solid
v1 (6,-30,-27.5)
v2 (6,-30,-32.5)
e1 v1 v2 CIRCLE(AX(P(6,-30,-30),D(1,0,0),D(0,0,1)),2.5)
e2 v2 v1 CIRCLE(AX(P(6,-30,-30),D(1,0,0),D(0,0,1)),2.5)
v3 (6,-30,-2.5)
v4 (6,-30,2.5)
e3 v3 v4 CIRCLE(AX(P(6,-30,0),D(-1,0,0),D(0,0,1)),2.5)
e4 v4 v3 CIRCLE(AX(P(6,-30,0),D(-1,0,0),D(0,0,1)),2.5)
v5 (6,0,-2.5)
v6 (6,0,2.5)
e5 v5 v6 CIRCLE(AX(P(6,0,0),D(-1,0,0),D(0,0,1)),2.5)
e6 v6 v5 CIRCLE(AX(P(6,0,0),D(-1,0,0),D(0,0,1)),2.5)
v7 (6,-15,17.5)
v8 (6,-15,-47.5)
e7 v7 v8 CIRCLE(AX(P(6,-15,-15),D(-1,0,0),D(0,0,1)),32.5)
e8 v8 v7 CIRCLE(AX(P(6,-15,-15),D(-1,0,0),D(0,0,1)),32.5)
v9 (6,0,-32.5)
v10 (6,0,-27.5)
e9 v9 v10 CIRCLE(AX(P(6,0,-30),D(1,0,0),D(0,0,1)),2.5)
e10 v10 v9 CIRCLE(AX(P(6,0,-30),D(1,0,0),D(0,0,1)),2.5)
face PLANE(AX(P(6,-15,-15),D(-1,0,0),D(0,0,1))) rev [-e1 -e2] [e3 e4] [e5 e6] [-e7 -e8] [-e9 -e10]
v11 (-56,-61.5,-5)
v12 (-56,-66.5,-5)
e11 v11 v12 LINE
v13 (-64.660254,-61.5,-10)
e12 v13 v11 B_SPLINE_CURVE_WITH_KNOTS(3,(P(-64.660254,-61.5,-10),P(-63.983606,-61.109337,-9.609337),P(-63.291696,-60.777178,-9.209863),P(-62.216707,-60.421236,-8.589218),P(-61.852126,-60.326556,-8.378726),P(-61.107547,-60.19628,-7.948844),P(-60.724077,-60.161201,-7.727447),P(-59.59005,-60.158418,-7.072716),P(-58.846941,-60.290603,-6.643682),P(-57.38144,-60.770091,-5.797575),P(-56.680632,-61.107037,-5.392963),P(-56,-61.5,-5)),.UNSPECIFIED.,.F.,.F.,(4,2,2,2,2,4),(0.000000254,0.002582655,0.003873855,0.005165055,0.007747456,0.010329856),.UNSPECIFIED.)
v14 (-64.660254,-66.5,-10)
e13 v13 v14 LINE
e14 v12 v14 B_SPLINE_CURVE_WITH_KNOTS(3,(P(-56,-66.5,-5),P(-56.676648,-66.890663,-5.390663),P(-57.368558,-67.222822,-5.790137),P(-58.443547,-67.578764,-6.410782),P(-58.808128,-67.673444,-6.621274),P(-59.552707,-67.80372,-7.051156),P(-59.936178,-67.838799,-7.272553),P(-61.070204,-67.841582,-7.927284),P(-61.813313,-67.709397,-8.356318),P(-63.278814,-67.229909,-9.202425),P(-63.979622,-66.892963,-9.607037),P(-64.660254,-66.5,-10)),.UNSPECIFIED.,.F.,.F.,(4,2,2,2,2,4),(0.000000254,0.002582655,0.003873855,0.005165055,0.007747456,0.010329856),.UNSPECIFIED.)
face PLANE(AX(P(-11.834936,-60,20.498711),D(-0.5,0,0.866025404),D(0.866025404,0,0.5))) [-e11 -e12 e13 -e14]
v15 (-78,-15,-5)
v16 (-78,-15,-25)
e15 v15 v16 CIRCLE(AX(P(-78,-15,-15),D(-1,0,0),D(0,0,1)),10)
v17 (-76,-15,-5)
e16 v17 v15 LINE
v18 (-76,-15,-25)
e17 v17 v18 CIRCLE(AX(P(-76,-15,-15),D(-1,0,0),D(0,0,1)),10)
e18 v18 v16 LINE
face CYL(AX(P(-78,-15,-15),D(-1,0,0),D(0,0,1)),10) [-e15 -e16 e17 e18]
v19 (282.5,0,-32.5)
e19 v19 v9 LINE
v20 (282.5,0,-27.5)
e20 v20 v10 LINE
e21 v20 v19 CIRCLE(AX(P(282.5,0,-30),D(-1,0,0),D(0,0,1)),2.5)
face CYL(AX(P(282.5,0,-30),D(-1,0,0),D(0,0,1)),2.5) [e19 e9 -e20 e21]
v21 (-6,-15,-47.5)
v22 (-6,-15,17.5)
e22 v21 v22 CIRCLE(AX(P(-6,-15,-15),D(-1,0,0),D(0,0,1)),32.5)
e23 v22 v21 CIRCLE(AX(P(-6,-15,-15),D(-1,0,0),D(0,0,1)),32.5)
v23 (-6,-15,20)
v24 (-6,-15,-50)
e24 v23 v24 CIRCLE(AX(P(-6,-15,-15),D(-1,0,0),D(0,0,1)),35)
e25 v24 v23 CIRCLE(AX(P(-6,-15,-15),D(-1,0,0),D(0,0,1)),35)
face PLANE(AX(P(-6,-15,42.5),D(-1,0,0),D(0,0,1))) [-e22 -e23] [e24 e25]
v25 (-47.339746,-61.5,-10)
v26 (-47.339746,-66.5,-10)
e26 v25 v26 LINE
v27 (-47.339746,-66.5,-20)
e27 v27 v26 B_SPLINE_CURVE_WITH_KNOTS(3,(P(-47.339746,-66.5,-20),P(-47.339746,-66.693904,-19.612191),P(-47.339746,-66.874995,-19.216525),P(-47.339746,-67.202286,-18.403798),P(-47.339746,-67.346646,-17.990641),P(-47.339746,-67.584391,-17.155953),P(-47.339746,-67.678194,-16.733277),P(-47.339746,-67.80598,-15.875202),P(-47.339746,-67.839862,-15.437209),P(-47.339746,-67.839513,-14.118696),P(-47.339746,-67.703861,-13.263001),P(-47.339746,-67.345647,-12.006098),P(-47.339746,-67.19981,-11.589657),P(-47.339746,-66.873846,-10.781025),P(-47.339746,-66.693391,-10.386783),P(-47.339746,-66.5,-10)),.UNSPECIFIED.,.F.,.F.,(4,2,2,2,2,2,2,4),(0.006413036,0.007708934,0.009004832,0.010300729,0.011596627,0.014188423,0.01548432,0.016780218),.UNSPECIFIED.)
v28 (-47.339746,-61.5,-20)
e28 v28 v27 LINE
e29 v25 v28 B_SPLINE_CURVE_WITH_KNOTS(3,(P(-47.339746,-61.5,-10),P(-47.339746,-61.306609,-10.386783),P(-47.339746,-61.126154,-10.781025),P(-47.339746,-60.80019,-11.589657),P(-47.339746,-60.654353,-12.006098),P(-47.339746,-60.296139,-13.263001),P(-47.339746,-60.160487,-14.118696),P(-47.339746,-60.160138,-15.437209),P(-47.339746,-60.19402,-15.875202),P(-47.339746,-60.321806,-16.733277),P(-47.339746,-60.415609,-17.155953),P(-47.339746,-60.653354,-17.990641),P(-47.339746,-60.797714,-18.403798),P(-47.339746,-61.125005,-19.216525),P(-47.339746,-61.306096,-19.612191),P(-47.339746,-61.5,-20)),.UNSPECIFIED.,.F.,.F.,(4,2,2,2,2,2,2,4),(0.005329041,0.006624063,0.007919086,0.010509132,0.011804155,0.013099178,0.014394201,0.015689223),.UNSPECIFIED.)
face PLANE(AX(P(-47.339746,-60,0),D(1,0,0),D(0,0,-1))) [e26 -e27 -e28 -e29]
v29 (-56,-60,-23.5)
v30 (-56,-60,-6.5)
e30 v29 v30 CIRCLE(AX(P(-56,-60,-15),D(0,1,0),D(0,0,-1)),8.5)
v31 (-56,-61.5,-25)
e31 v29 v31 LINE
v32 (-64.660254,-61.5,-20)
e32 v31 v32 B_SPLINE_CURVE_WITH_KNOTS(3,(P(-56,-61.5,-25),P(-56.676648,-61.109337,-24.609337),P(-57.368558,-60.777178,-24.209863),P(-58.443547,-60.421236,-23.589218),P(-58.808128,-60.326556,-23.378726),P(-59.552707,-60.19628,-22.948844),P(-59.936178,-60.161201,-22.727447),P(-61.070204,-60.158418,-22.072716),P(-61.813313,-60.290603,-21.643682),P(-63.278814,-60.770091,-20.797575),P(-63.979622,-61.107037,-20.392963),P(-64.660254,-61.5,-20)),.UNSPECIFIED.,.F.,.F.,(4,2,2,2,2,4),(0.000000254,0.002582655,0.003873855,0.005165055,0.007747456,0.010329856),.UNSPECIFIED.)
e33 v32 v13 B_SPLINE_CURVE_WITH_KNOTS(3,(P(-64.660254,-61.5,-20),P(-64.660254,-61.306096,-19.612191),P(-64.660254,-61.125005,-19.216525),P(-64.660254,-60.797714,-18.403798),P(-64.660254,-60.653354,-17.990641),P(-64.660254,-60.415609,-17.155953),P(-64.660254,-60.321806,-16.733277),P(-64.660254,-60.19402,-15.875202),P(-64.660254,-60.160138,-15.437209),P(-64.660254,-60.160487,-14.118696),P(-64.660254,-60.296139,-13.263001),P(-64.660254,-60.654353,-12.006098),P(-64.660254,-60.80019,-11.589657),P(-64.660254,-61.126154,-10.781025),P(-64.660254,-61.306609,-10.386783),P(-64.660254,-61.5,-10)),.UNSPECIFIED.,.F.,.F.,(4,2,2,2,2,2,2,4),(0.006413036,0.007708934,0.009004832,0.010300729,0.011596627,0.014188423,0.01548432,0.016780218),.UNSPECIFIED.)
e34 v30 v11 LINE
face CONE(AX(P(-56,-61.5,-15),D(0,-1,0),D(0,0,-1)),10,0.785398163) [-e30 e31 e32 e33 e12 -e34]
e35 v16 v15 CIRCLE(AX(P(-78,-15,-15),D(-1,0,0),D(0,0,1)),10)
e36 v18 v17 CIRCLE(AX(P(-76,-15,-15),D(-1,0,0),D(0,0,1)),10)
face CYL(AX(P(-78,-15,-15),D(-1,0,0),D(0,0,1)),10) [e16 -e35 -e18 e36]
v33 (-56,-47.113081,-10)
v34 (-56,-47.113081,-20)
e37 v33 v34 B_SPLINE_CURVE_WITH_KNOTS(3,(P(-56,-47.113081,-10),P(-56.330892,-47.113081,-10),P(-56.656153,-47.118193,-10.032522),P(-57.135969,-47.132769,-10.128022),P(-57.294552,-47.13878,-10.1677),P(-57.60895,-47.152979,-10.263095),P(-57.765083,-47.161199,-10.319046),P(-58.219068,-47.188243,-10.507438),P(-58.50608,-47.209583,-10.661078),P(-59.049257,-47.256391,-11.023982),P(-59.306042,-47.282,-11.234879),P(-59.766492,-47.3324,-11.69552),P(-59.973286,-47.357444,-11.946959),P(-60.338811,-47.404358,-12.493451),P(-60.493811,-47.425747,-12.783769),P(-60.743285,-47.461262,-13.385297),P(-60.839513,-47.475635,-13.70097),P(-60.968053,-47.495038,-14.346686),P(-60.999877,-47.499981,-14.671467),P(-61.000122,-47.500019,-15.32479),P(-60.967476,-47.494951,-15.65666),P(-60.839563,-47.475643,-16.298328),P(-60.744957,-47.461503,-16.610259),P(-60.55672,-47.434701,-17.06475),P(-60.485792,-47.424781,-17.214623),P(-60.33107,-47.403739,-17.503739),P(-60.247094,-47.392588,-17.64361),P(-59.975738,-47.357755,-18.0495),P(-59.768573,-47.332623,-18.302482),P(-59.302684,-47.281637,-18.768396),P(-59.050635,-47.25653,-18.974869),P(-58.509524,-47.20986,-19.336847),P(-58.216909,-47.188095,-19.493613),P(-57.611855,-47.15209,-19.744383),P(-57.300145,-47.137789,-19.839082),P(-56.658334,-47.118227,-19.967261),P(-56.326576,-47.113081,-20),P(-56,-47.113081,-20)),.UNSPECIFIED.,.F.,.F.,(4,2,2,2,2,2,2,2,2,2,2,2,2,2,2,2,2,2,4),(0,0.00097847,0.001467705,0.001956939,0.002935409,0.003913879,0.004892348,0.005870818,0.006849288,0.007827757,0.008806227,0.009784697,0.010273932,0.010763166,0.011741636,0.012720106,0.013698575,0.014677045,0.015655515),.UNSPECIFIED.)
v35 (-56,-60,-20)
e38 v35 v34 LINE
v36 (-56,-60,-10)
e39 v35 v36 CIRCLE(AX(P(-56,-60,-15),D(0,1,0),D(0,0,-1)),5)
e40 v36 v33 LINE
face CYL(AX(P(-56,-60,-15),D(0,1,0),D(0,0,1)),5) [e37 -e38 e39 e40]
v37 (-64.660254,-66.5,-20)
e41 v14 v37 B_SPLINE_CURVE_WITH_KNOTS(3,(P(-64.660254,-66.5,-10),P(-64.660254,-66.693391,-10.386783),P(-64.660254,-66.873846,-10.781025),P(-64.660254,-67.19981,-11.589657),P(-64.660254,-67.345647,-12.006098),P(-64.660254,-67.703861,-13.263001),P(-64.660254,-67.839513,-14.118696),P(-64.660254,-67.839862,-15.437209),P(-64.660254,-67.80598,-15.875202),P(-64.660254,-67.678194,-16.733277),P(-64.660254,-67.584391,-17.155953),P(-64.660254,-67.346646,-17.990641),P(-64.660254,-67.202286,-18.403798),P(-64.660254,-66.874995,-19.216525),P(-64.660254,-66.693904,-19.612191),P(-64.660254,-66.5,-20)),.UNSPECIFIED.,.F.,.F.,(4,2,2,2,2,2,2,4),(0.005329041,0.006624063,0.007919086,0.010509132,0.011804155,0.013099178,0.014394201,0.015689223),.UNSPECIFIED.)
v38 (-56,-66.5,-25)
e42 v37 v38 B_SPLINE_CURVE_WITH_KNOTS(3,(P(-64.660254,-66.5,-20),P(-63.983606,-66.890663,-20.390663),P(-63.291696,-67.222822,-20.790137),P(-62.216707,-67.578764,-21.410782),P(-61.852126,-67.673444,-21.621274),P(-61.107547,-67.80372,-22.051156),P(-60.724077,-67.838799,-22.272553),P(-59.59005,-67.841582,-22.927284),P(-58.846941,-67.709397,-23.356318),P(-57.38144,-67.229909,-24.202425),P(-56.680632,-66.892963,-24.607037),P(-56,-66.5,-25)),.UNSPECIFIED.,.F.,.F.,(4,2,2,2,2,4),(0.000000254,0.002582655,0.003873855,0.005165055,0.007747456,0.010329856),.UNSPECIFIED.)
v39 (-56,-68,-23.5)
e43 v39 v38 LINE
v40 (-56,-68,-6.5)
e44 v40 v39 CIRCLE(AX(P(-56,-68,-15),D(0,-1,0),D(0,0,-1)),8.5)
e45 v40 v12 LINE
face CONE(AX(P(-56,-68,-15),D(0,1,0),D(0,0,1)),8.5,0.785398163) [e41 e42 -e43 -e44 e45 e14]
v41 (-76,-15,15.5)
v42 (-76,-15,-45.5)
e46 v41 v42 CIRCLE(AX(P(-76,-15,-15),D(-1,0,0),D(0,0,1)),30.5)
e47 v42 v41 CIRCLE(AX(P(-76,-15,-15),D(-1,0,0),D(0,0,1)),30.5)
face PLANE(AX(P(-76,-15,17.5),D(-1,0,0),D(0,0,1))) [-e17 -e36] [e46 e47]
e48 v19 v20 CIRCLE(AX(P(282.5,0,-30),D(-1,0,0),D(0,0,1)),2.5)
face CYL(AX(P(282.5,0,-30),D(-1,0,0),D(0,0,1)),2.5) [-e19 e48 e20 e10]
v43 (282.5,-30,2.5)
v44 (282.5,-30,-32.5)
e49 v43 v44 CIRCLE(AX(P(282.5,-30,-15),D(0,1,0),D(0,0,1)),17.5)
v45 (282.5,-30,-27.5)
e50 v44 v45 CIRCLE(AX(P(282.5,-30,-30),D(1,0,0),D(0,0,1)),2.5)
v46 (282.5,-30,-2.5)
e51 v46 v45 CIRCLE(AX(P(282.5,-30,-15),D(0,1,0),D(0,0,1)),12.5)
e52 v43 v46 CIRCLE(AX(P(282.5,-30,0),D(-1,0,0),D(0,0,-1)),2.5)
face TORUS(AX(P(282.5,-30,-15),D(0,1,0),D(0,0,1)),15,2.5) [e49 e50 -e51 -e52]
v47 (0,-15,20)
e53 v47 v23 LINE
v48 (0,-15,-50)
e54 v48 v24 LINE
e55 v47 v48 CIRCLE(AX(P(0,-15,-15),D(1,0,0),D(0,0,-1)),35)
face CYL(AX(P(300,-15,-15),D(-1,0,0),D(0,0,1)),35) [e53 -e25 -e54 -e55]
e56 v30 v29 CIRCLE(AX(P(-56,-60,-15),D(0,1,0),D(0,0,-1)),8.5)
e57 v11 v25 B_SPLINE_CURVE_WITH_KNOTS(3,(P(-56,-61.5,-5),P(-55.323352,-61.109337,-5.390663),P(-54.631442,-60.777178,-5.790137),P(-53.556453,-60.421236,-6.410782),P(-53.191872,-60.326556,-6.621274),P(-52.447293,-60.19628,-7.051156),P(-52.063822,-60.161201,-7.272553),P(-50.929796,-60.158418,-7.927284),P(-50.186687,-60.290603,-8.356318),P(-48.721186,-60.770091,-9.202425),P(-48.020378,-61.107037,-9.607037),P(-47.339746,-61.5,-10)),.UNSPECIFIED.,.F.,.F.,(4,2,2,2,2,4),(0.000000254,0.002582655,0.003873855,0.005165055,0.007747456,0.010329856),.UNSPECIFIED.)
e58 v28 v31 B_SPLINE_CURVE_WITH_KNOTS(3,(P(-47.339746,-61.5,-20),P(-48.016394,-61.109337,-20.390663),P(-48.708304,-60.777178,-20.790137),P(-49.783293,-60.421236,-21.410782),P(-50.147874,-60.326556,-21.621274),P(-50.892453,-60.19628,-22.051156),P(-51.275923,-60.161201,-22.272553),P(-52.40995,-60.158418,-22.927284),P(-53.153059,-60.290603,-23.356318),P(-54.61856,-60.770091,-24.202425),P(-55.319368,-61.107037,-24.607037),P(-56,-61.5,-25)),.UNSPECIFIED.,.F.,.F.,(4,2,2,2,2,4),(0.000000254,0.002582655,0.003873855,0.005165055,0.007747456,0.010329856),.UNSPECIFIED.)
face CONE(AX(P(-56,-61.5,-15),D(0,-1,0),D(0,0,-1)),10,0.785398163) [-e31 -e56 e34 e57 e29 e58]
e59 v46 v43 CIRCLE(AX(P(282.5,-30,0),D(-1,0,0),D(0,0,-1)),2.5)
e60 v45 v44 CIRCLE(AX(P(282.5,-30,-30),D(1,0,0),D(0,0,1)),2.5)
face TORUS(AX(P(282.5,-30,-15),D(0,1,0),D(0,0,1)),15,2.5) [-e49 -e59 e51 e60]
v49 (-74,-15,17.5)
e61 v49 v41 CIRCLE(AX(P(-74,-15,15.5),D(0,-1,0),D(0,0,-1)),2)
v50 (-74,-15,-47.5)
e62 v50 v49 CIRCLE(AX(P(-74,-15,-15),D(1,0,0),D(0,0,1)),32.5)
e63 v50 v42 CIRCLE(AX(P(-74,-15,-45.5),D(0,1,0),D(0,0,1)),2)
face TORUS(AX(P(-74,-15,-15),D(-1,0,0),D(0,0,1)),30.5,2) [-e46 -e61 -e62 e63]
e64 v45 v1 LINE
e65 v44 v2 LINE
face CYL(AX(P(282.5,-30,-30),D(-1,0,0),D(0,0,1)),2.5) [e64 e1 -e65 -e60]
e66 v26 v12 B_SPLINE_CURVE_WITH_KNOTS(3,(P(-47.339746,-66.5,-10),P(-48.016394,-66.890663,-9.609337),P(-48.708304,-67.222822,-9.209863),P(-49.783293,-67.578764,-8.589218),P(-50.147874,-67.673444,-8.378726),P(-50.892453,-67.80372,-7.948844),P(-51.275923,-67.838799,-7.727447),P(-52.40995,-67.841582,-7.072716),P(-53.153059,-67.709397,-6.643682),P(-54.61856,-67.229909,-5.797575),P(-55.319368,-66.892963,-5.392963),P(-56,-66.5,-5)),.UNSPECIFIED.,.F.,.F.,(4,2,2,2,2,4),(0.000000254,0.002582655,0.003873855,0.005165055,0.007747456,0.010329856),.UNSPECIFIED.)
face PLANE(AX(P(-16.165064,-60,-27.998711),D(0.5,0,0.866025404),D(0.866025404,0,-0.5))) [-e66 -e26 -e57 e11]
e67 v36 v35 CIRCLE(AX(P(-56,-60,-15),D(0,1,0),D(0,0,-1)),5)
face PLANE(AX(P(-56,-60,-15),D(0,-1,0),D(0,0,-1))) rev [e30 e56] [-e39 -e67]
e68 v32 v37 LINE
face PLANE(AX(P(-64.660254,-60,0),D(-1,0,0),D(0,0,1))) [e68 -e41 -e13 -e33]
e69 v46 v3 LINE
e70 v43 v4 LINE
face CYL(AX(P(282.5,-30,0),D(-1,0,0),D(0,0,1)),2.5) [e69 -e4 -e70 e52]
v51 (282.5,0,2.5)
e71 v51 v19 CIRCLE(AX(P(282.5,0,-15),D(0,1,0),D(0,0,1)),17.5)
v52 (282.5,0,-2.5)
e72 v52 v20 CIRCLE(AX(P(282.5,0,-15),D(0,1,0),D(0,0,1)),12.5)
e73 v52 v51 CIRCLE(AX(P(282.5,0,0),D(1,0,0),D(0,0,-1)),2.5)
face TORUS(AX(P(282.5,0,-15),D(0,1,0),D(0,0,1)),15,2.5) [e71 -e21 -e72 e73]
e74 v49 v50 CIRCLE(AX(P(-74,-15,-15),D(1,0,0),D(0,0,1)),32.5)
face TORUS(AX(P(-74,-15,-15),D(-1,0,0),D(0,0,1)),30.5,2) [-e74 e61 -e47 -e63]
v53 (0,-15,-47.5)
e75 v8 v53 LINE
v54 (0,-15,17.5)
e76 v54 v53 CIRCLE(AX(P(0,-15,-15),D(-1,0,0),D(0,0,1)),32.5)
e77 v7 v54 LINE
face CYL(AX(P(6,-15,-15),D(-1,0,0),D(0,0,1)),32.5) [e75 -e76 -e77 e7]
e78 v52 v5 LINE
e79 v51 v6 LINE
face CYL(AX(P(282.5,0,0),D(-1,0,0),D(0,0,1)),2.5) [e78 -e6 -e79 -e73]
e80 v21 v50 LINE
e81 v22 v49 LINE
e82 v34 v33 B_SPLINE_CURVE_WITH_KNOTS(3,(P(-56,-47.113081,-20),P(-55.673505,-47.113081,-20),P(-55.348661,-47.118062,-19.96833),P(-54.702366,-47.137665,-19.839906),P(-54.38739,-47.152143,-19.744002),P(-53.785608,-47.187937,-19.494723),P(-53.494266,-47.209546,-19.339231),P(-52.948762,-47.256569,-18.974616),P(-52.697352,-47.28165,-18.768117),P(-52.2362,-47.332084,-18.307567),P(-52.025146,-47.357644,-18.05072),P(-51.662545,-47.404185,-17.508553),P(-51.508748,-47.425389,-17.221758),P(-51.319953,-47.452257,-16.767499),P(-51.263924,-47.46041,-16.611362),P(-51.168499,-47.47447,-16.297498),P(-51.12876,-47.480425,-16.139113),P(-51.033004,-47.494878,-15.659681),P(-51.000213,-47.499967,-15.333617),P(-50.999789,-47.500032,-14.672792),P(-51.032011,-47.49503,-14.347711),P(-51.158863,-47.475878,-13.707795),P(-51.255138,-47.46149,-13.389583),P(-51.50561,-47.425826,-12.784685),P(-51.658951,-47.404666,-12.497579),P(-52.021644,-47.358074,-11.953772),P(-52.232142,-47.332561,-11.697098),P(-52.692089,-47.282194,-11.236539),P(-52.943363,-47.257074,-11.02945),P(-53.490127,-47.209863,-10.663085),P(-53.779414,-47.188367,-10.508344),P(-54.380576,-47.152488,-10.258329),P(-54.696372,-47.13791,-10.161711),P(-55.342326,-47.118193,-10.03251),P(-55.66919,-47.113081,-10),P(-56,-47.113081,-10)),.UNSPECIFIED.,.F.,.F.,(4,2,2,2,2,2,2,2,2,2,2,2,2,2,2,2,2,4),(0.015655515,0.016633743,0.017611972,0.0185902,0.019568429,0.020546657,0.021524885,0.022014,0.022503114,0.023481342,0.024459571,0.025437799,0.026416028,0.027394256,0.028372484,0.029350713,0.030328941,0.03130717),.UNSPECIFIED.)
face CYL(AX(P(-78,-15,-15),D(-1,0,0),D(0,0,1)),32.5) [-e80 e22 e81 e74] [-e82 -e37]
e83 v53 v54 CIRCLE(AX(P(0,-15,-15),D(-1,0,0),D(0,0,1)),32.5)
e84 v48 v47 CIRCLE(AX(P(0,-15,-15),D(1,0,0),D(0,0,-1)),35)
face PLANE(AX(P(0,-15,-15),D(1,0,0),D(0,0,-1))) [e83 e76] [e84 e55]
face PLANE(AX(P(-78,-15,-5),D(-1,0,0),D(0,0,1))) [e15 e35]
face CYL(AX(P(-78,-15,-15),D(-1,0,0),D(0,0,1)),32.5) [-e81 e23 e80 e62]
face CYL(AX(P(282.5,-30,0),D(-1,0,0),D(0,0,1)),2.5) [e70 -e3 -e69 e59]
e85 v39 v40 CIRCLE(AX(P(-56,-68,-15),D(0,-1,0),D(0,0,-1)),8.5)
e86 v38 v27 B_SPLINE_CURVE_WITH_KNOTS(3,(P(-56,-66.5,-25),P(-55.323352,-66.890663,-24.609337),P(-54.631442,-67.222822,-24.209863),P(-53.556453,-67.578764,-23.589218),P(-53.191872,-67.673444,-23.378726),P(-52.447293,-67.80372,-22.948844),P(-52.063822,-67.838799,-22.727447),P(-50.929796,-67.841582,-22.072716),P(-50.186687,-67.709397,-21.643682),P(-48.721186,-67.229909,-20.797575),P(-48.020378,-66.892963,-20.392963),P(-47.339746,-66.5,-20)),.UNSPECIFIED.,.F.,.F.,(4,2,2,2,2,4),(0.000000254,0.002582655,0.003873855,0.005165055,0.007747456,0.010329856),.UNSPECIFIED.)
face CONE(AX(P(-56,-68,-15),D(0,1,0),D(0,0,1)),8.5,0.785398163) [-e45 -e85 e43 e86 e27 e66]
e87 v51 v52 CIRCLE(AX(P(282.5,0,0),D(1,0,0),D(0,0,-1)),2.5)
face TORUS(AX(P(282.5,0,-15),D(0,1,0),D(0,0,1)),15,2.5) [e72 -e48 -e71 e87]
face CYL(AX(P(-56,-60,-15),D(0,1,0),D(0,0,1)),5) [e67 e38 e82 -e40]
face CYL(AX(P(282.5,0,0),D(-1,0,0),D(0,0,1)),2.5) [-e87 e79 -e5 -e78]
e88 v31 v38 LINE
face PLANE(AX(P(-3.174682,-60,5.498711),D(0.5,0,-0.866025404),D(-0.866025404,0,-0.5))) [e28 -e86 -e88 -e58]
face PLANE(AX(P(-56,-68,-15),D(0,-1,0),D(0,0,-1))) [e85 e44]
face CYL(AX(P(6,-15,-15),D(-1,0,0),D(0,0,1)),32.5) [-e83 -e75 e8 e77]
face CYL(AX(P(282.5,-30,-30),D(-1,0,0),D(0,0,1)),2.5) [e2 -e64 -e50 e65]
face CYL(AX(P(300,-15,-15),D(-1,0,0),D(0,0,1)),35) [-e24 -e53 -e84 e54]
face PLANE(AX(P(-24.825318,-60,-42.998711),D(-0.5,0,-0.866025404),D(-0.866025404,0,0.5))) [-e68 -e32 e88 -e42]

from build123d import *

# Parameters (mm, degrees)
SKETCH1_R           = 2.5
SKETCH3_R           = 32.5
BOSS_EXTRUDE1_DEPTH = 6
SKETCH5_R           = 4.5
CUT_EXTRUDE1_DEPTH  = 6
CIRPATTERN1_COUNT   = 6
SKETCH6_R           = 5
BOSS_EXTRUDE2_DEPTH = 45
SKETCH7_R           = 10
BOSS_EXTRUDE3_DEPTH = 8
CHAMFER1_SIZE       = 1.5
CUT_EXTRUDE2_START  = -8
CUT_EXTRUDE2_DEPTH  = 8
FILLET1_R           = 2
SKETCH9_R           = 57.5
SKETCH9_R_2         = 35
CUT_EXTRUDE3_DEPTH  = 323.720467373


with BuildPart() as part:
    # Sweep1: sweep along a path in Sketch2
    with BuildLine(Plane(origin=(0, 0, 0), x_dir=(1, 0, 0), z_dir=(0, 1, 0))) as sweep1_path:
        Line((0, 0), (282.5, 0))
        ThreePointArc((282.5, 0), (297.5, 15), (282.5, 30))
        Line((282.5, 30), (0, 30))
    # Sketch1 → Sweep1 (sweep)
    with BuildSketch(Plane(origin=(0, 0, 0), x_dir=(0, 0, -1), z_dir=(1, 0, 0))):
        Circle(SKETCH1_R)
    sweep1 = sweep(path=sweep1_path.line)

    # Sketch3 → Boss-Extrude1 (add)
    with BuildSketch(Plane.ZY):
        with Locations((-15, -15)):
            Circle(SKETCH3_R)
    extrude(amount=-BOSS_EXTRUDE1_DEPTH)

    # Mirror3: Sweep1 across plane
    add(sweep1.mirror(Plane.ZX.offset(-15)))

    # Sketch4 → Revolve1 (revolve)
    with BuildSketch(Plane(origin=(0, -15, 0), x_dir=(-1, 0, 0), z_dir=(0, 1, 0))):
        Polygon((0, -15), (0, 42.5), (6, 42.5), (6, 17.5), (76, 17.5), (76, -5), (78, -5), (78, -15), align=None)
    revolve(axis=Axis((-78, -15, -15), (1, 0, 0)))

    # Sketch5 → Cut-Extrude1 (cut)
    with BuildSketch(Plane.ZY.offset(6)):
        with Locations((-15, 32)):
            Circle(SKETCH5_R)
    cut_extrude1 = extrude(amount=-CUT_EXTRUDE1_DEPTH, mode=Mode.SUBTRACT)

    # CirPattern1: Cut-Extrude1 ×6 about axis
    cirpattern1_axis = Axis((0, -15, -15), (1, 0, 0))
    for i in range(1, CIRPATTERN1_COUNT):
        add(cut_extrude1.rotate(cirpattern1_axis, i * 360 / CIRPATTERN1_COUNT), mode=Mode.SUBTRACT)

    # Sketch6 → Boss-Extrude2 (add)
    with BuildSketch(Plane(origin=(0, -15, 0), x_dir=(-1, 0, 0), z_dir=(0, 1, 0))):
        with Locations(Location((56, -15, 0), (0, 0, 90))):
            Circle(SKETCH6_R)
    extrude(amount=-BOSS_EXTRUDE2_DEPTH)

    # Sketch7 → Boss-Extrude3 (add)
    with BuildSketch(Plane.XZ.offset(60)):
        with Locations(Location((-56, -15, 0), (0, 0, 270))):
            Circle(SKETCH7_R)
    extrude(amount=BOSS_EXTRUDE3_DEPTH)

    # Chamfer1
    chamfer1_edges = [part.edges().sort_by_distance(p)[0] for p in [
        (-56, -60, -5),
        (-56, -68, -5),
    ]]
    chamfer(chamfer1_edges, length=CHAMFER1_SIZE)

    # Sketch8 → Cut-Extrude2 (cut)
    with BuildSketch(Plane.XZ.offset(68).offset(CUT_EXTRUDE2_START)):
        with BuildLine():
            Line((-64.660254038, -20), (-64.660254038, -10))
            ThreePointArc((-64.660254038, -10), (-66, -15), (-64.660254038, -20))
        make_face()
        with BuildLine():
            Line((-64.660254038, -10), (-56, -5))
            ThreePointArc((-56, -5), (-61, -6.339745962), (-64.660254038, -10))
        make_face()
        with BuildLine():
            ThreePointArc((-47.339745962, -10), (-51, -6.339745962), (-56, -5))
            Line((-56, -5), (-47.339745962, -10))
        make_face()
        with BuildLine():
            ThreePointArc((-46, -15), (-46.340741737, -12.411809549), (-47.339745962, -10))
            Line((-47.339745962, -10), (-47.339745962, -20))
            ThreePointArc((-47.339745962, -20), (-46.340741737, -17.588190451), (-46, -15))
        make_face()
        with BuildLine():
            ThreePointArc((-56, -25), (-51, -23.660254038), (-47.339745962, -20))
            Line((-47.339745962, -20), (-56, -25))
        make_face()
        with BuildLine():
            Line((-56, -25), (-64.660254038, -20))
            ThreePointArc((-64.660254038, -20), (-61, -23.660254038), (-56, -25))
        make_face()
    extrude(amount=CUT_EXTRUDE2_DEPTH, mode=Mode.SUBTRACT)

    # Fillet1
    fillet1_edges = [part.edges().sort_by_distance(p)[0] for p in [
        (-76, -15, -47.5),
    ]]
    fillet(fillet1_edges, radius=FILLET1_R)

    # Sketch9 → Cut-Extrude3 (cut, through all)
    with BuildSketch(Plane.ZY.offset(6)):
        with Locations((-15, -15)):
            Circle(SKETCH9_R)
        with Locations((-15, -15)):
            Circle(SKETCH9_R_2, mode=Mode.SUBTRACT)
    extrude(amount=-CUT_EXTRUDE3_DEPTH, mode=Mode.SUBTRACT)


solid = part.part
